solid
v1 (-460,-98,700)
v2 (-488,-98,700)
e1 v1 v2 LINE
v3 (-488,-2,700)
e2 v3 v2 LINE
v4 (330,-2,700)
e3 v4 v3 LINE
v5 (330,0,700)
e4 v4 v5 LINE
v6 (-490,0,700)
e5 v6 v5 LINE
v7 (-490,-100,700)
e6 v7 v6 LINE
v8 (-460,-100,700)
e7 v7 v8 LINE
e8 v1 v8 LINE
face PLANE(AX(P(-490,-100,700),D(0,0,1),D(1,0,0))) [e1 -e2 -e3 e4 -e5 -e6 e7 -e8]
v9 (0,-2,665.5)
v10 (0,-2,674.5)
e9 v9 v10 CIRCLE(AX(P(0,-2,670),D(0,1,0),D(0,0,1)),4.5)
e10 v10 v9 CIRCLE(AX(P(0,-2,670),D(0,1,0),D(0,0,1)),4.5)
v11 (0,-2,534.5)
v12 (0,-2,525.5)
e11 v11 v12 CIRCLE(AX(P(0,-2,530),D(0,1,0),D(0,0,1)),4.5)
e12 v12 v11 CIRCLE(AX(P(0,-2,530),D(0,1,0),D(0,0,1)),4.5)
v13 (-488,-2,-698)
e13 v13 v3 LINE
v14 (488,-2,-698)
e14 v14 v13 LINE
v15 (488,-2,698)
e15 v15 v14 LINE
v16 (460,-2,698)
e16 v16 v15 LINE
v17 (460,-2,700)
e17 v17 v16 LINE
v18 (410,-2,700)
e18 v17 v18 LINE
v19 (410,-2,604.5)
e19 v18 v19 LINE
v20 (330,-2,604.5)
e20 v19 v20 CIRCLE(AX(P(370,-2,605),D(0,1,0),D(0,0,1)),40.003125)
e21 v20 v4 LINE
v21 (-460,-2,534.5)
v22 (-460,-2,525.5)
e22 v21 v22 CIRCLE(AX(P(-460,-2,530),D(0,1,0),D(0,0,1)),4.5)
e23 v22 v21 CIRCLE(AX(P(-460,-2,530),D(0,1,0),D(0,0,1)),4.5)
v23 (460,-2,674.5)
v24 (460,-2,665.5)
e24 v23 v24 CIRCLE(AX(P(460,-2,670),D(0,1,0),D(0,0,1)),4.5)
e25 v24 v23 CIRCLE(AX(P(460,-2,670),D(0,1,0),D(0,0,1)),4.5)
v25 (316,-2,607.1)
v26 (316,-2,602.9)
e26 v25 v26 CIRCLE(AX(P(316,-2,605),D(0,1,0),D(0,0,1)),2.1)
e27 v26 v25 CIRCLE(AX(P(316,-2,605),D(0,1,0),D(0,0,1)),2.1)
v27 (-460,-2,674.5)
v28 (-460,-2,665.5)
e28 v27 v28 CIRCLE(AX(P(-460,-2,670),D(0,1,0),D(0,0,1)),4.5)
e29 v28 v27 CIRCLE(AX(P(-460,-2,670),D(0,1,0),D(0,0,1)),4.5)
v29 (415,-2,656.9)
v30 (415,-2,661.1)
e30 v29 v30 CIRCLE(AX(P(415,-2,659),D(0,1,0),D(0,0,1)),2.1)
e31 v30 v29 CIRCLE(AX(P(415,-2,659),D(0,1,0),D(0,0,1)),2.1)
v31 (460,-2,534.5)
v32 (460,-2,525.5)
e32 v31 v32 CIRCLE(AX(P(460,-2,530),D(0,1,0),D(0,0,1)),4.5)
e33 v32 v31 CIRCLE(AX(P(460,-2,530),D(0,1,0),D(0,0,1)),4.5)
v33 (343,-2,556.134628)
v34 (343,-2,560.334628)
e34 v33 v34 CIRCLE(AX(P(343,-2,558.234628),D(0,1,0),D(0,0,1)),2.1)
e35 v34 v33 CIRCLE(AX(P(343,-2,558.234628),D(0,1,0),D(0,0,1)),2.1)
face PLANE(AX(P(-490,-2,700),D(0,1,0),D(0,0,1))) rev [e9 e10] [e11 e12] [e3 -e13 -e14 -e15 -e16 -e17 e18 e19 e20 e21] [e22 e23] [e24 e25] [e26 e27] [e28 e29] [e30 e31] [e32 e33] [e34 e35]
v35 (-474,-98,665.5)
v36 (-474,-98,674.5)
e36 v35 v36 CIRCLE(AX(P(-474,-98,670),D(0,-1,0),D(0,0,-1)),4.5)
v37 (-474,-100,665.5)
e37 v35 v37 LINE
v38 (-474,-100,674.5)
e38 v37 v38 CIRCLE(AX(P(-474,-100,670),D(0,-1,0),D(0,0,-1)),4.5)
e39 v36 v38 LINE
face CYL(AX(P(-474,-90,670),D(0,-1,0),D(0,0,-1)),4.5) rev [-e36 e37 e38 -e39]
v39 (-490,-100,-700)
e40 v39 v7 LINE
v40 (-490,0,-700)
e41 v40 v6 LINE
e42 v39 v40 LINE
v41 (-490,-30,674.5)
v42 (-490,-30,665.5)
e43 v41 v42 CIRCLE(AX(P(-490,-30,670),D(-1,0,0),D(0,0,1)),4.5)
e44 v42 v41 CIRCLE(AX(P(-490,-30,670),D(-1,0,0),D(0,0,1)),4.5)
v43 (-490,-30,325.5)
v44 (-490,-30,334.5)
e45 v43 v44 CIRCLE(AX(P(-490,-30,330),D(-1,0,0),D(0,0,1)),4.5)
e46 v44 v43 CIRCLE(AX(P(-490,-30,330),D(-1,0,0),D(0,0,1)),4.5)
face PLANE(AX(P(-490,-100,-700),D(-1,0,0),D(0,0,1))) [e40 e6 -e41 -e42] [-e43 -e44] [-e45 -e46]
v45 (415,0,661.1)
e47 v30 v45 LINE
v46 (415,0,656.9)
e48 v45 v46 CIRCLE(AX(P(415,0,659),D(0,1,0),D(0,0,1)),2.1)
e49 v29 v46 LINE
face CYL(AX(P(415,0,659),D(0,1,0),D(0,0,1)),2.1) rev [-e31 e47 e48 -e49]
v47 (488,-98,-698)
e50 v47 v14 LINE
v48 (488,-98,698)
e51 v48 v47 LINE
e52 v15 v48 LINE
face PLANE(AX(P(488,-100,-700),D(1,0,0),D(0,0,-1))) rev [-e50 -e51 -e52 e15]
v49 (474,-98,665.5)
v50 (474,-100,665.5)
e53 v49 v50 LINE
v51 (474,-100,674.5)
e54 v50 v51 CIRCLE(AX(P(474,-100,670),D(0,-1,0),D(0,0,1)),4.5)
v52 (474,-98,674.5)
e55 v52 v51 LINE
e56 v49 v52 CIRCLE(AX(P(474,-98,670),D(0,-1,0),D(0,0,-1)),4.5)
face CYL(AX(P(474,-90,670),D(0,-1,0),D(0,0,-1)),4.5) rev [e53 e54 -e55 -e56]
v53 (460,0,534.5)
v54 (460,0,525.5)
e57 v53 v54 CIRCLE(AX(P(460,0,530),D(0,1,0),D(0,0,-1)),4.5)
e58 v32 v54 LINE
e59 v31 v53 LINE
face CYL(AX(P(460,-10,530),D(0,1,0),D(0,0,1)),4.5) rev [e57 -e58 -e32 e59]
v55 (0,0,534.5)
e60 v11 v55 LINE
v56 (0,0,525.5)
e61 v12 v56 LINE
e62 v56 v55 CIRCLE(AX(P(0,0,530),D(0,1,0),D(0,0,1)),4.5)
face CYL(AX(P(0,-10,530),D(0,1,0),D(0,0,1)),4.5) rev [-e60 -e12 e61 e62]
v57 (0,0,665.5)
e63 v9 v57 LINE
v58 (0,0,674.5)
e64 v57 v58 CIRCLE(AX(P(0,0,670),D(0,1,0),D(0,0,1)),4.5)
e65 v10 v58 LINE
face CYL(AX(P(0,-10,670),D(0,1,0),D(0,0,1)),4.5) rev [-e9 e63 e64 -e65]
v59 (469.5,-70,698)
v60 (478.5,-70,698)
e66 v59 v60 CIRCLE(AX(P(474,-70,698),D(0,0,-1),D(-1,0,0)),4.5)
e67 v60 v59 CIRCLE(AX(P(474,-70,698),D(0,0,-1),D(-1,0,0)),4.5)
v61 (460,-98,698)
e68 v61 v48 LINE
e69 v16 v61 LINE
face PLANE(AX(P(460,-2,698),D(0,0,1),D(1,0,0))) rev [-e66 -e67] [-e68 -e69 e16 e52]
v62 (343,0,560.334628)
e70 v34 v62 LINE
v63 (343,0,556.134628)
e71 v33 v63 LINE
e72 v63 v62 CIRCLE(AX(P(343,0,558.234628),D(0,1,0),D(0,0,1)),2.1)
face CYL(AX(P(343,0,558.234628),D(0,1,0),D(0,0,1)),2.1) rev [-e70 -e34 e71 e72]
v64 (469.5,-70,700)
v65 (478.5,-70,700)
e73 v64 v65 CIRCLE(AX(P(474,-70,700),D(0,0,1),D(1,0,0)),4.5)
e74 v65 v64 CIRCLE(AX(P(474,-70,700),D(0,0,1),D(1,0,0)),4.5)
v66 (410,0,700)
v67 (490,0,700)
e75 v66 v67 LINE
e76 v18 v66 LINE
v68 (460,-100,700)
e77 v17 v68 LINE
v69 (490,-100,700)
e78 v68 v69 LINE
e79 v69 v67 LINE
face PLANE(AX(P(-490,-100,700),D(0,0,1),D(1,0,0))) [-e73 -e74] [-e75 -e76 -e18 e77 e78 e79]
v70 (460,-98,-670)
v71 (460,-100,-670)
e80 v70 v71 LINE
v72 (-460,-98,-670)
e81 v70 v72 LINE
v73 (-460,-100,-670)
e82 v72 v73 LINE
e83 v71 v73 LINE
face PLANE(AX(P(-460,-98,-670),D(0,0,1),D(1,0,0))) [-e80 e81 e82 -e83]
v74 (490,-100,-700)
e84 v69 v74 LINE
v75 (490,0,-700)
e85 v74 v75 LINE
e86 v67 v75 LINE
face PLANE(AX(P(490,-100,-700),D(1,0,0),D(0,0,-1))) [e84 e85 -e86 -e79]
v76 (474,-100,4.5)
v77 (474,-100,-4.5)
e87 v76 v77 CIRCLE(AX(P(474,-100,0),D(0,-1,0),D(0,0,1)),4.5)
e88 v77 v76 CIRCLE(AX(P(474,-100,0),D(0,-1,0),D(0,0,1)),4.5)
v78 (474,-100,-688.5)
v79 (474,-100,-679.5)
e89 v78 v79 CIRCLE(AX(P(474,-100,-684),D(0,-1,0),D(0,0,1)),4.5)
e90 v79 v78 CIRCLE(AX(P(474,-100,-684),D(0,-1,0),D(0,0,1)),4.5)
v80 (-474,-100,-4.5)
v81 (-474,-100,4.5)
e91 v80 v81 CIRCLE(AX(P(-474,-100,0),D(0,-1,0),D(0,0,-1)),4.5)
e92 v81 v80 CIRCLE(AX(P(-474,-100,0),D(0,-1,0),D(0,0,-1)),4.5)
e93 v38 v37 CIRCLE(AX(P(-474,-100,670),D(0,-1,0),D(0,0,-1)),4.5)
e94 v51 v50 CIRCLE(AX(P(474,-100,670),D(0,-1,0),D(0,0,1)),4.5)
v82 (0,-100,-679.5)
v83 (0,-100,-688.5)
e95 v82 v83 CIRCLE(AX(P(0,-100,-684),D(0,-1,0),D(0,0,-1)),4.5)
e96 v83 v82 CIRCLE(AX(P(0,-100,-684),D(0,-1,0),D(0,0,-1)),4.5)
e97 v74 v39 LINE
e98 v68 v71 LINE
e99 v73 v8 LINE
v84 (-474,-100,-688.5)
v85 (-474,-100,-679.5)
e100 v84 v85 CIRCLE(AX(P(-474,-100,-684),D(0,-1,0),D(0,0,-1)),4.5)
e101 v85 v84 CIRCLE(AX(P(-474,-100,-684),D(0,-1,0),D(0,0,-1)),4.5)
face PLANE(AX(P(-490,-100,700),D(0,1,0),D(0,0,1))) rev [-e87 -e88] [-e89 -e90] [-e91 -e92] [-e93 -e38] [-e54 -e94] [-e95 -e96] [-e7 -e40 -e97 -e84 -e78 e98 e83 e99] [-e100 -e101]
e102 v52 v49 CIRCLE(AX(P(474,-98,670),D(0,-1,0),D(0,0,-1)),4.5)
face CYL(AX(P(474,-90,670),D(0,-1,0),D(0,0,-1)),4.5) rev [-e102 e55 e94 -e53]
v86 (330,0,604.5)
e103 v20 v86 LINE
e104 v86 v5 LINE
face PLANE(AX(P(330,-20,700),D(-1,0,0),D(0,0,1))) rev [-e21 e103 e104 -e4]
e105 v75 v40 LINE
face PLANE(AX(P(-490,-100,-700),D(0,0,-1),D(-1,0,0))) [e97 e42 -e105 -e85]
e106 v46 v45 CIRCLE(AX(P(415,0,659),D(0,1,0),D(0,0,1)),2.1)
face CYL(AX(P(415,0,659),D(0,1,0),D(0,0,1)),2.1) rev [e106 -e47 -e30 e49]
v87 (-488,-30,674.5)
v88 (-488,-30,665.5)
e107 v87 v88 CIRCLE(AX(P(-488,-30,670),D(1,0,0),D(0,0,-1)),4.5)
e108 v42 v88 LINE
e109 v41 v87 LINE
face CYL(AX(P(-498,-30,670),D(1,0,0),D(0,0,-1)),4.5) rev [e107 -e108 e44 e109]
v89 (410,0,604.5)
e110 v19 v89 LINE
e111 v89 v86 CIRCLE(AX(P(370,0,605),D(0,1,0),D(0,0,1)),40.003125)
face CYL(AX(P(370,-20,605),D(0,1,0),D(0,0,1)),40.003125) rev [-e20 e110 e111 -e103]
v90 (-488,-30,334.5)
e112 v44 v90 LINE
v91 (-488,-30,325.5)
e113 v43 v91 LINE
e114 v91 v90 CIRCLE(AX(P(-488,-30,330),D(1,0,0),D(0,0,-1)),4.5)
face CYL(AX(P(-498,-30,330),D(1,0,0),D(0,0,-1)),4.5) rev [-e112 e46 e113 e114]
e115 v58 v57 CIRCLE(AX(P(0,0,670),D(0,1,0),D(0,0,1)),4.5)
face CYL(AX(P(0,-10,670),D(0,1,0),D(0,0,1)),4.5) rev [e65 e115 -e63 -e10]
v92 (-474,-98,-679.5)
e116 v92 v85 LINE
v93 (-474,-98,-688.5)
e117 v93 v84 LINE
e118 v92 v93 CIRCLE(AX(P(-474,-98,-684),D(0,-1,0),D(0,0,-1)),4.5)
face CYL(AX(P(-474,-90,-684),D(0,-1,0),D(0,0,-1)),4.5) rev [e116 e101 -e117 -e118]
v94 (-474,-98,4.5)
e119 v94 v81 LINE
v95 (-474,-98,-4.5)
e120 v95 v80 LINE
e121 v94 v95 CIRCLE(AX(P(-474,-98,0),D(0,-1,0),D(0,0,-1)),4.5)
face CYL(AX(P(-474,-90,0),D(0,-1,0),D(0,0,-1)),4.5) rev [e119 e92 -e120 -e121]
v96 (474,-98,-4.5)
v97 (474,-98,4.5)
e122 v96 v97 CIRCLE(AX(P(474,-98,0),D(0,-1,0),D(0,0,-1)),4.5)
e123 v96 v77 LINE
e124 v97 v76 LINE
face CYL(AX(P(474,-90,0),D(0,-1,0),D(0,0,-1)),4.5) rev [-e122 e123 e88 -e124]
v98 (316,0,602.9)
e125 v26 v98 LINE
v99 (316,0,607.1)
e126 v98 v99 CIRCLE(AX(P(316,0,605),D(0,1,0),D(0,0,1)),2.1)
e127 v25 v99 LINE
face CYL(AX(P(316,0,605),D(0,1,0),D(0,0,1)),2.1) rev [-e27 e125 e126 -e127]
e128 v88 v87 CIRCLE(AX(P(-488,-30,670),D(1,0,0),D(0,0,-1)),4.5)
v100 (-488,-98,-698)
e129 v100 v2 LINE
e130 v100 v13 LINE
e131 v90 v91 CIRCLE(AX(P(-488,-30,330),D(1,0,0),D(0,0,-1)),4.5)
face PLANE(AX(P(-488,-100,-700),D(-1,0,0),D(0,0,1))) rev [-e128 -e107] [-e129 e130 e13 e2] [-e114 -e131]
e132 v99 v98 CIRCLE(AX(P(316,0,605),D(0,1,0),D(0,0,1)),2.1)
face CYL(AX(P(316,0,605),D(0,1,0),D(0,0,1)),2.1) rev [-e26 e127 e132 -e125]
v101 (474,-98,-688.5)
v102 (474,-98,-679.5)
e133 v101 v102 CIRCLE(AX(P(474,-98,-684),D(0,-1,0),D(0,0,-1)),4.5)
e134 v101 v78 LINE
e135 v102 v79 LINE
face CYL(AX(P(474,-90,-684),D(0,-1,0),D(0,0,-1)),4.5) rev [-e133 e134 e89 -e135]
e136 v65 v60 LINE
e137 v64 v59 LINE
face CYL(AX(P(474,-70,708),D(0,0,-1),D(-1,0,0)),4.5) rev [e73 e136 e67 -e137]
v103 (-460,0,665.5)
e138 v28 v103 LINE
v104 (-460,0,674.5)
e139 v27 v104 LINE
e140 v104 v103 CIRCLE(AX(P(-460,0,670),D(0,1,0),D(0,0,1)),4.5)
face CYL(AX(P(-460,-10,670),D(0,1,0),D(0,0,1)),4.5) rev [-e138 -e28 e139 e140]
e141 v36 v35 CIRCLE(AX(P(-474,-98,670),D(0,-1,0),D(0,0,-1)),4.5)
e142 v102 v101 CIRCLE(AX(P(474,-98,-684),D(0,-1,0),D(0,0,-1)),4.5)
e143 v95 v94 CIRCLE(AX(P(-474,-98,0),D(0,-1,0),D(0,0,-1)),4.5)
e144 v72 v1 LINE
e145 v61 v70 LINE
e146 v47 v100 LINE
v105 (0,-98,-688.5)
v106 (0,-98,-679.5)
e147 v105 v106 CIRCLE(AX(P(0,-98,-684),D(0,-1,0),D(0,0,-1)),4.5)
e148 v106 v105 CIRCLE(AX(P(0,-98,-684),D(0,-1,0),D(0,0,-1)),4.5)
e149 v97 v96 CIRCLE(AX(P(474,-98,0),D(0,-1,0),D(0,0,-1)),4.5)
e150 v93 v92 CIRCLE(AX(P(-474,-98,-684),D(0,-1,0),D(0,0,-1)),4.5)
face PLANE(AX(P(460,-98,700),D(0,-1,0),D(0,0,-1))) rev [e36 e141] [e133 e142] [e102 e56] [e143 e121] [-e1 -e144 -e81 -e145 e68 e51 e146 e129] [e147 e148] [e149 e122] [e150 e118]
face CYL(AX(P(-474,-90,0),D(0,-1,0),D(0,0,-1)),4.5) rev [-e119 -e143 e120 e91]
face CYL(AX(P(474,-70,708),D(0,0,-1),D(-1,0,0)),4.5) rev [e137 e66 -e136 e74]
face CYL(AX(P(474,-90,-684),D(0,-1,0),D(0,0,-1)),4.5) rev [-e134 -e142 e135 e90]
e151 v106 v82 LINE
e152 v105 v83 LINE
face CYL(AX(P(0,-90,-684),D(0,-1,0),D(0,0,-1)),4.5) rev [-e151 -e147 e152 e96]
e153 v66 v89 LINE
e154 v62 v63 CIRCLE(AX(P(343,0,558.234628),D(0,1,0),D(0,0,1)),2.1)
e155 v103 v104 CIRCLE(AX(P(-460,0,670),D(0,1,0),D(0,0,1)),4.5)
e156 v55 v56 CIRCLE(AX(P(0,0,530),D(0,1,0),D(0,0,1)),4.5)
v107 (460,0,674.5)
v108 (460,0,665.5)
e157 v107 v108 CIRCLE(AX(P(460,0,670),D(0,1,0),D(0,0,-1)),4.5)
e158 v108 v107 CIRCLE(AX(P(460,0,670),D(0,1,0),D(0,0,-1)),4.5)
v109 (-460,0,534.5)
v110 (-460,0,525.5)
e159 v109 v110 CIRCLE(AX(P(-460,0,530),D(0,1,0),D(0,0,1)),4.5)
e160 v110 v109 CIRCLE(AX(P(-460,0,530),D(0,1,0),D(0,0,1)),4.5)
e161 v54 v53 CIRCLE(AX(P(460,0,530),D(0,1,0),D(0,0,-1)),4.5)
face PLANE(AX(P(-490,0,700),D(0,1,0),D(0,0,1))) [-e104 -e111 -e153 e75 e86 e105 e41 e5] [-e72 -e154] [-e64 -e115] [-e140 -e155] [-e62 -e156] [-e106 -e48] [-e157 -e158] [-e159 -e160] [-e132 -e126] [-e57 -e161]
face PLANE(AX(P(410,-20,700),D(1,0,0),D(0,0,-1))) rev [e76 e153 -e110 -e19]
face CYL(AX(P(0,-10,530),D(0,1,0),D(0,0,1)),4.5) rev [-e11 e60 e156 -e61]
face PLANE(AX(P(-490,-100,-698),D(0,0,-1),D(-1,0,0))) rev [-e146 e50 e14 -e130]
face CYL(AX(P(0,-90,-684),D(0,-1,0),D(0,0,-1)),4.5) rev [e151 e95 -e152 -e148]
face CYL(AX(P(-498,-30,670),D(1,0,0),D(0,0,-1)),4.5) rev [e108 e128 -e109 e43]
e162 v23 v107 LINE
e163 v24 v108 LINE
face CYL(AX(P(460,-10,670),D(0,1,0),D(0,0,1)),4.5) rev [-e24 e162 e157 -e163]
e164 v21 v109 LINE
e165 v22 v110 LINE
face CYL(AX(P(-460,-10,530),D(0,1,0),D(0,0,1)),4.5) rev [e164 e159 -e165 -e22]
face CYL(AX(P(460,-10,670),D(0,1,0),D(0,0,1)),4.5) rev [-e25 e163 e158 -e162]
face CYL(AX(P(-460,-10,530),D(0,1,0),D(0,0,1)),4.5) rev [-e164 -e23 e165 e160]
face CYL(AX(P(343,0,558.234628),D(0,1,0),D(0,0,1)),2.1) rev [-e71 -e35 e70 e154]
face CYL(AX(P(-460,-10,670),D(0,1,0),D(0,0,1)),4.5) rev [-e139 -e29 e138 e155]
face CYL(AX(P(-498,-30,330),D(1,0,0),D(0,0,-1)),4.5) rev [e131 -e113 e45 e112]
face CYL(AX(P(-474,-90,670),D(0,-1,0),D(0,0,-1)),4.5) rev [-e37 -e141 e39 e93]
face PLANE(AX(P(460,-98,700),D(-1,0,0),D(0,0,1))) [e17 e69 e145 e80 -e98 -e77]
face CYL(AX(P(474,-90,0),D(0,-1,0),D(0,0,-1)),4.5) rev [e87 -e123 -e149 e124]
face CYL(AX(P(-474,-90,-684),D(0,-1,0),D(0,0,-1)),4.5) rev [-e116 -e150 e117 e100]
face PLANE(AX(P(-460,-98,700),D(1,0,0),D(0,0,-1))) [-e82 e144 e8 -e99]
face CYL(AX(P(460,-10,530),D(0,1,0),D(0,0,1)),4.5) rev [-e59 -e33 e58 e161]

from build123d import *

# Parameters (mm, degrees)
SKETCH_1_W             = 980
SKETCH_1_H             = 1400
EXTRUDE_1_DEPTH        = 100
SHELL_1_T              = -2
CUT_EXTRUDE_1_DEPTH    = 20
SKETCH_5_W             = 976
SKETCH_5_H             = 98
CUT_EXTRUDE_2_DEPTH    = 20
EXTRUDE_2_DEPTH        = 2
SKETCH_7_W             = 2
SKETCH_7_H             = 96
EXTRUDE_3_DEPTH        = 28
SKETCH_8_R             = 4.5
CUT_EXTRUDE_3_DEPTH    = 10
SKETCH_9_R             = 4.5
CUT_EXTRUDE_4_DEPTH    = 10
SKETCH_10_R            = 4.5
CUT_EXTRUDE_5_DEPTH    = 10
SKETCH_11_R            = 4.5
CUT_EXTRUDE_6_DEPTH    = 10
HOLE_WIZARD_M5_1_D     = 4.2
HOLE_WIZARD_M5_1_DEPTH = 1260
HOLE_WIZARD_M5_1_TIP   = 1.2618073


with BuildPart() as part:
    # 草图1 → 凸台-拉伸1 (new body)
    with BuildSketch(Plane(origin=(0, 0, 0), x_dir=(1, 0, 0), z_dir=(0, 1, 0))):
        Rectangle(SKETCH_1_W, SKETCH_1_H)
    extrude(amount=-EXTRUDE_1_DEPTH)

    # 抽壳1
    shell_1_openings = [part.faces().sort_by_distance(p)[0] for p in [
        (0, -100, 0),
    ]]
    offset(amount=SHELL_1_T, openings=shell_1_openings, kind=Kind.INTERSECTION)

    # 草图3 → 切除-拉伸1 (cut)
    with BuildSketch(Plane(origin=(0, 0, 0), x_dir=(1, 0, 0), z_dir=(0, 1, 0))):
        with BuildLine():
            Line((330, -700), (410, -700))
            Line((410, -700), (410, -604.5))
            ThreePointArc((410, -604.5), (370, -564.996875122), (330, -604.5))
            Line((330, -604.5), (330, -700))
        make_face()
    extrude(amount=-CUT_EXTRUDE_1_DEPTH, mode=Mode.SUBTRACT)

    # 草图5 → 切除-拉伸2 (cut)
    with BuildSketch(Plane.XY.offset(700)):
        with Locations((0, -51)):
            Rectangle(SKETCH_5_W, SKETCH_5_H)
    extrude(amount=-CUT_EXTRUDE_2_DEPTH, mode=Mode.SUBTRACT)

    # 草图6 → 凸台-拉伸2 (add)
    with BuildSketch(Plane.XZ.offset(100)):
        Polygon((490, 700), (490, -700), (-490, -700), (-490, 700), (-460, 700), (-460, -670), (460, -670), (460, 700), align=None)
    extrude(amount=-EXTRUDE_2_DEPTH)

    # 草图7 → 凸台-拉伸3 (add)
    with BuildSketch(Plane.ZY.offset(-488)):
        with Locations((699, -50)):
            Rectangle(SKETCH_7_W, SKETCH_7_H)
    extrude(amount=EXTRUDE_3_DEPTH)

    # 草图8 → 切除-拉伸3 (cut)
    with BuildSketch(Plane.XZ.offset(100)):
        with Locations(Location((-474, 670, 0), (0, 0, 270))):
            Circle(SKETCH_8_R)
        with Locations(Location((-474, 0, 0), (0, 0, 270))):
            Circle(SKETCH_8_R)
        with Locations(Location((-474, -684, 0), (0, 0, 270))):
            Circle(SKETCH_8_R)
        with Locations(Location((0, -684, 0), (0, 0, 270))):
            Circle(SKETCH_8_R)
        with Locations(Location((474, -684, 0), (0, 0, 270))):
            Circle(SKETCH_8_R)
        with Locations(Location((474, 0, 0), (0, 0, 270))):
            Circle(SKETCH_8_R)
        with Locations(Location((474, 670, 0), (0, 0, 270))):
            Circle(SKETCH_8_R)
    extrude(amount=-CUT_EXTRUDE_3_DEPTH, mode=Mode.SUBTRACT)

    # 草图9 → 切除-拉伸4 (cut)
    with BuildSketch(Plane(origin=(0, 0, 698), x_dir=(-1, 0, 0), z_dir=(0, 0, -1))):
        with Locations((-474, -70)):
            Circle(SKETCH_9_R)
    extrude(amount=-CUT_EXTRUDE_4_DEPTH, mode=Mode.SUBTRACT)

    # 草图10 → 切除-拉伸5 (cut)
    with BuildSketch(Plane(origin=(-488, 0, 0), x_dir=(0, 0, -1), z_dir=(1, 0, 0))):
        with Locations((-670, -30)):
            Circle(SKETCH_10_R)
        with Locations((-330, -30)):
            Circle(SKETCH_10_R)
    extrude(amount=-CUT_EXTRUDE_5_DEPTH, mode=Mode.SUBTRACT)

    # 草图11 → 切除-拉伸6 (cut)
    with BuildSketch(Plane(origin=(0, 0, 0), x_dir=(1, 0, 0), z_dir=(0, 1, 0))):
        with Locations(Location((-460, -670, 0), (0, 0, 270))):
            Circle(SKETCH_11_R)
        with Locations(Location((0, -530, 0), (0, 0, 270))):
            Circle(SKETCH_11_R)
        with Locations(Location((460, -530, 0), (0, 0, 270))):
            Circle(SKETCH_11_R)
        with Locations(Location((-460, -530, 0), (0, 0, 270))):
            Circle(SKETCH_11_R)
        with Locations(Location((0, -670, 0), (0, 0, 270))):
            Circle(SKETCH_11_R)
        with Locations(Location((460, -670, 0), (0, 0, 270))):
            Circle(SKETCH_11_R)
    extrude(amount=-CUT_EXTRUDE_6_DEPTH, mode=Mode.SUBTRACT)

    # M5 螺纹孔1
    with Locations(Plane(origin=(0, 0, 0), x_dir=(-1, 0, 0), z_dir=(0, 1, 0))):
        with Locations((-343, 558.234628196), (-316, 605), (-415, 659)):
            Hole(HOLE_WIZARD_M5_1_D / 2, depth=HOLE_WIZARD_M5_1_DEPTH)
            with Locations((0, 0, -(HOLE_WIZARD_M5_1_DEPTH + HOLE_WIZARD_M5_1_TIP / 2))):  # 118° drill point
                Cone(0, HOLE_WIZARD_M5_1_D / 2, HOLE_WIZARD_M5_1_TIP, mode=Mode.SUBTRACT)


solid = part.part
